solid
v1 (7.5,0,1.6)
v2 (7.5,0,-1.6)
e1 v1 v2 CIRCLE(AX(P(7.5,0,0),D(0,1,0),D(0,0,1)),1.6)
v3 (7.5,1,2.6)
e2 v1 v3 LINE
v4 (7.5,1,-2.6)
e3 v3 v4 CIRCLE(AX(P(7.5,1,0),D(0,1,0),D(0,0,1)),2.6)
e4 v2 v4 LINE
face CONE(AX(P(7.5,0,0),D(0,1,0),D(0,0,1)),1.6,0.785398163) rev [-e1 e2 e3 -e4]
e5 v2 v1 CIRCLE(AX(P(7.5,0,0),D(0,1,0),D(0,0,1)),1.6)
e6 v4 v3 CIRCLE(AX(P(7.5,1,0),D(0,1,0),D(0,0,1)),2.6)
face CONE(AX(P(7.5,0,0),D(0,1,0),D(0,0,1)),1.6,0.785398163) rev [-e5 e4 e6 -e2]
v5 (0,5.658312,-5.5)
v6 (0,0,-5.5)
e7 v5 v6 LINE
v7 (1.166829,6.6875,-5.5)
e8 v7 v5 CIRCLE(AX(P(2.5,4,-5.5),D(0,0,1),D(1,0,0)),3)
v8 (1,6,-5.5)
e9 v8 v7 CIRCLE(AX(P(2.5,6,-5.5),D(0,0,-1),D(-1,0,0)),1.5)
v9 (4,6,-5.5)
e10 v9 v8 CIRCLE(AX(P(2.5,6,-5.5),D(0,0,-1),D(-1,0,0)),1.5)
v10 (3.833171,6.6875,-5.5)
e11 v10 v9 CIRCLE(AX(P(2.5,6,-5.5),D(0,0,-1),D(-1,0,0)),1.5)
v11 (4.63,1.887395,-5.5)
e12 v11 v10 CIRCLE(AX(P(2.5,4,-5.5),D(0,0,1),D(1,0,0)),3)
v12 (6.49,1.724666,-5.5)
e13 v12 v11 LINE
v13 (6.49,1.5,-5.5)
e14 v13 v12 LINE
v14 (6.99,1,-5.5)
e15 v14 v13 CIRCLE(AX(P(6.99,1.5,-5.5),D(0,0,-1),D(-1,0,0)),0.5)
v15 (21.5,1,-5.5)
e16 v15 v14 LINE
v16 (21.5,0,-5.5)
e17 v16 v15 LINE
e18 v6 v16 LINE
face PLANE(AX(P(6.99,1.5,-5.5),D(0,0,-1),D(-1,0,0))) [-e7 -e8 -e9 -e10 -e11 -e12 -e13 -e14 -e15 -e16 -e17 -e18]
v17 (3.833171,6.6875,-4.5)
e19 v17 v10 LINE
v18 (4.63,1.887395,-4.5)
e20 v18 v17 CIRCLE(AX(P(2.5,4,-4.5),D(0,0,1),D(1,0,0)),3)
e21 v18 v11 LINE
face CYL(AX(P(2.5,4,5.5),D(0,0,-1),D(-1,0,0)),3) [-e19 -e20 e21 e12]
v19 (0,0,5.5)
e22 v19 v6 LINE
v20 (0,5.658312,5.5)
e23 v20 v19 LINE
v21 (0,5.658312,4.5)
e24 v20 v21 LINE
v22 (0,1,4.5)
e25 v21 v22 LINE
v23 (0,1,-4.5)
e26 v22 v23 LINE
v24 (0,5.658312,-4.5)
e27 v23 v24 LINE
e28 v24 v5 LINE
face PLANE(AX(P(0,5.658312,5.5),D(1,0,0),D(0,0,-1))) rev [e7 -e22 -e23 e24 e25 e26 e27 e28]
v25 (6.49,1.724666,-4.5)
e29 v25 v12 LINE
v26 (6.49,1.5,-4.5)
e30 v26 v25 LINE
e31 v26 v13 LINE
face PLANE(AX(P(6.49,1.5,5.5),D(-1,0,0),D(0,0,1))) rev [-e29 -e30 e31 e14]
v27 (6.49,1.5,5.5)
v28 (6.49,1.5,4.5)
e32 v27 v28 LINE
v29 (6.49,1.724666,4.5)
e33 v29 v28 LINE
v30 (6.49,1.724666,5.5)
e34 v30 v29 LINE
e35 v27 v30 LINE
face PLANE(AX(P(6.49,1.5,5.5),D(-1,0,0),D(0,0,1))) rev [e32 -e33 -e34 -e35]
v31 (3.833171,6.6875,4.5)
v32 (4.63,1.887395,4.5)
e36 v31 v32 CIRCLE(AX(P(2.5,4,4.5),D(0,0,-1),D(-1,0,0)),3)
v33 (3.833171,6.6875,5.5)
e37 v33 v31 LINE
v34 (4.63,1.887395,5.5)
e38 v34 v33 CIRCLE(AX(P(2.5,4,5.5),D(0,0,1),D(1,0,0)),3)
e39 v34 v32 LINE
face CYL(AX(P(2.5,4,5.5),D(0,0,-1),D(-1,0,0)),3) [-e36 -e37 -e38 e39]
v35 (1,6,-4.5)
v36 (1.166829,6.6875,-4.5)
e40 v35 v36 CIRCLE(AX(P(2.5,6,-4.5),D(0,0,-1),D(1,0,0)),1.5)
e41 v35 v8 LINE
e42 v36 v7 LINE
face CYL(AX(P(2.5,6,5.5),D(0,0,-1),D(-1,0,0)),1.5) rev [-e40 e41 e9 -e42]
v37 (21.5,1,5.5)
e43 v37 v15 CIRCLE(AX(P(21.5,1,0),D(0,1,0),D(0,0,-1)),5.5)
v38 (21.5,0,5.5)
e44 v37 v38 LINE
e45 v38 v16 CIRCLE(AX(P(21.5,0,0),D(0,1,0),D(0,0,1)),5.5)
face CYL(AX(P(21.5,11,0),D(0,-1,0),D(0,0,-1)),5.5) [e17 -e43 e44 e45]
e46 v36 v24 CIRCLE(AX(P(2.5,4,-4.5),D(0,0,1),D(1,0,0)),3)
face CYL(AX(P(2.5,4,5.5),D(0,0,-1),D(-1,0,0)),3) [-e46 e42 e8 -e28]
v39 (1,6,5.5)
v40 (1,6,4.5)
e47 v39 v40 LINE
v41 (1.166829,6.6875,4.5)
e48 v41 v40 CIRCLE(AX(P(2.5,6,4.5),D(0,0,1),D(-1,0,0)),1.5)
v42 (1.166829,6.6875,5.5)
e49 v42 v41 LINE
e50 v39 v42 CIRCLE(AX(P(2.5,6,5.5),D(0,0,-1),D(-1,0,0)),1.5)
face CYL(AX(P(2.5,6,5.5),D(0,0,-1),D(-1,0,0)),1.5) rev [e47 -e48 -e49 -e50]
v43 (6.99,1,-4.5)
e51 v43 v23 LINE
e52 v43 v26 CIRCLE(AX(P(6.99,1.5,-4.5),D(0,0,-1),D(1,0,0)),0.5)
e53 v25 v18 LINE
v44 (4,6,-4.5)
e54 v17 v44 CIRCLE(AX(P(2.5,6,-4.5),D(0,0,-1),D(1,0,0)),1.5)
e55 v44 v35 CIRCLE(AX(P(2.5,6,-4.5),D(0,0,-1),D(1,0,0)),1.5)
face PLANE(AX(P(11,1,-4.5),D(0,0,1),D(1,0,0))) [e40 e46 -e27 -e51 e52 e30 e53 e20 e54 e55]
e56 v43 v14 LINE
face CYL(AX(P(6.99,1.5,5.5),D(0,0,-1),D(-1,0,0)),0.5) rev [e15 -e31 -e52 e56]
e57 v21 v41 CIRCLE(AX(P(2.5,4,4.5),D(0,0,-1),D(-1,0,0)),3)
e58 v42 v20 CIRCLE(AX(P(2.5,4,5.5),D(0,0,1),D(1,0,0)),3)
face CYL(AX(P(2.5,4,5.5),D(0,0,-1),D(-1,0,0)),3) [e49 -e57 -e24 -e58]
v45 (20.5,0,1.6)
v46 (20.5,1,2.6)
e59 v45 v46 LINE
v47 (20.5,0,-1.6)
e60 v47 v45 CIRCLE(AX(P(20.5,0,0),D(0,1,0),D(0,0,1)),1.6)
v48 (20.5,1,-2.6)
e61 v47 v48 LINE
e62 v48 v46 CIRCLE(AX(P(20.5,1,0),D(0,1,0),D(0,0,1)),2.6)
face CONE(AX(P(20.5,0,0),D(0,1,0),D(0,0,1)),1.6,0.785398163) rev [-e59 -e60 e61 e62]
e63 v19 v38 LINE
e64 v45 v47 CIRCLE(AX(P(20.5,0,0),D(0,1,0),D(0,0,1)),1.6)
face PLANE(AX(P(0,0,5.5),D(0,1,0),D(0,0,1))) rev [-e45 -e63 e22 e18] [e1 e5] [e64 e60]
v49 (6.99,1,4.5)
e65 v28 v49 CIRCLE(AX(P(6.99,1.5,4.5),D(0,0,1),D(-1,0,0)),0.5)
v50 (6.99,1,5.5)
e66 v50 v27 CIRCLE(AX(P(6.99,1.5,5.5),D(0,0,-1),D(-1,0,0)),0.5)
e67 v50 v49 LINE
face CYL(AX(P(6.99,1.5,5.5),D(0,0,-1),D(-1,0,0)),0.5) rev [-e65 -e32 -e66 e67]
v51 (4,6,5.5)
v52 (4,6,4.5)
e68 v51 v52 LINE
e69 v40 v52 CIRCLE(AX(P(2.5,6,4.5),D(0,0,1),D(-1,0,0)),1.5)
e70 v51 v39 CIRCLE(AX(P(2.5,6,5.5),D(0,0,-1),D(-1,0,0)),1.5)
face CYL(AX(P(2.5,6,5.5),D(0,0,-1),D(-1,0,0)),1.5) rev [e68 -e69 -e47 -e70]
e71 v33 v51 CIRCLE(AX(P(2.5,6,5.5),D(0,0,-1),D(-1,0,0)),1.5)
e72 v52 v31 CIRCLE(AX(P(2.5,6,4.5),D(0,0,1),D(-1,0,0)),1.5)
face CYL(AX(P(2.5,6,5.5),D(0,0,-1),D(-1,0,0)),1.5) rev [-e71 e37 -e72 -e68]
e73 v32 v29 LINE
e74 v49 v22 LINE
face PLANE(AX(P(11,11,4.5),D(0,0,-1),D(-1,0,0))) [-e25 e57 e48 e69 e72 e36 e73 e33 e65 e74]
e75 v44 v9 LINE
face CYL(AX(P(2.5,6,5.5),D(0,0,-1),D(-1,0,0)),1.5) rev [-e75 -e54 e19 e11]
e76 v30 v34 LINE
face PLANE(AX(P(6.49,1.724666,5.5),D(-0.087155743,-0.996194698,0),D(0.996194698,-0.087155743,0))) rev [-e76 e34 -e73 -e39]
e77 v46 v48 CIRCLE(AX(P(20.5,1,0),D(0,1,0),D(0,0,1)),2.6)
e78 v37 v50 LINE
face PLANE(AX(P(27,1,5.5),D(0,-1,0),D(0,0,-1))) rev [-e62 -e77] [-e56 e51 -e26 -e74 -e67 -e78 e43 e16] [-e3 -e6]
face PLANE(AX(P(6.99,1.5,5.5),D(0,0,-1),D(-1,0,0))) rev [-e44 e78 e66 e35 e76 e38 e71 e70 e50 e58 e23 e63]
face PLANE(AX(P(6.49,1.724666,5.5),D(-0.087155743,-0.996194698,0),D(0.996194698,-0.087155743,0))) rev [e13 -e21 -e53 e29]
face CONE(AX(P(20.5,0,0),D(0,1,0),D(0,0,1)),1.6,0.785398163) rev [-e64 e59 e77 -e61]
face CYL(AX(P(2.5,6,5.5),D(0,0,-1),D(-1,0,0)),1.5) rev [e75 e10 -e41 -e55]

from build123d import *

# Parameters (mm, degrees)
EXTRUDE_1_DEPTH      = 5.5
EXTRUDE_1_DEPTH_BACK = 5.5
SKETCH_2_W           = 108
SKETCH_2_H           = 22
CUT_EXTRUDE_1_DEPTH  = 11
SKETCH_4_W           = 9
SKETCH_4_H           = 10
CUT_EXTRUDE_2_DEPTH  = 11


with BuildPart() as part:
    # 草图1 → 凸台-拉伸1 (new, two sides: drawn at the far end of the back side and taken through both)
    with BuildSketch(Plane.XY.offset(-EXTRUDE_1_DEPTH_BACK)):
        with BuildLine():
            Line((0, 0), (27, 0))
            Line((27, 0), (27, 1))
            Line((27, 1), (6.99, 1))
            ThreePointArc((6.99, 1), (6.636446609, 1.146446609), (6.49, 1.5))
            Line((6.49, 1.5), (6.49, 1.724666059))
            Line((6.49, 1.724666059), (4.63, 1.887394973))
            ThreePointArc((4.63, 1.887394973), (5.459499899, 4.491284383), (3.833170563, 6.6875))
            ThreePointArc((3.833170563, 6.6875), (2.5, 4.5), (1.166829437, 6.6875))
            ThreePointArc((1.166829437, 6.6875), (0.515533844, 6.249865346), (0, 5.658312395))
            Line((0, 5.658312395), (0, 0))
        make_face()
    extrude(amount=EXTRUDE_1_DEPTH + EXTRUDE_1_DEPTH_BACK)

    # 草图2 → 切除-拉伸1 (cut)
    with BuildSketch(Plane(origin=(0, 0, 0), x_dir=(1, 0, 0), z_dir=(0, 1, 0))):
        Rectangle(SKETCH_2_W, SKETCH_2_H)
        with BuildLine():
            Line((0, 5.5), (0, -5.5))
            Line((0, -5.5), (21.5, -5.5))
            ThreePointArc((21.5, -5.5), (27, 0), (21.5, 5.5))
            Line((21.5, 5.5), (0, 5.5))
        make_face(mode=Mode.SUBTRACT)
    extrude(amount=CUT_EXTRUDE_1_DEPTH, mode=Mode.SUBTRACT)

    # 草图4 → 切除-拉伸2 (cut)
    with BuildSketch(Plane(origin=(0, 0, 0), x_dir=(0, 0, -1), z_dir=(1, 0, 0))):
        with Locations((0, 6)):
            Rectangle(SKETCH_4_W, SKETCH_4_H)
    extrude(amount=CUT_EXTRUDE_2_DEPTH, mode=Mode.SUBTRACT)

    # 草图3 → 切除-旋转1 (revolve, cut)
    with BuildSketch(Plane.XY, mode=Mode.PRIVATE) as cut_revolve_1_sk:
        Polygon((7.5, 1), (10.1, 1), (9.1, 0), (7.5, 0), align=None)
    revolve(cut_revolve_1_sk.sketch.rotate(Axis((7.5, 0, 0), (0, 1, 0)), 270), axis=Axis((7.5, 0, 0), (0, 1, 0)), mode=Mode.SUBTRACT)

    # 草图5 → 切除-旋转2 (revolve, cut)
    with BuildSketch(Plane.XY, mode=Mode.PRIVATE) as cut_revolve_2_sk:
        Polygon((20.5, 1), (23.1, 1), (22.1, 0), (20.5, 0), align=None)
    revolve(cut_revolve_2_sk.sketch.rotate(Axis((20.5, 0, 0), (0, 1, 0)), 270), axis=Axis((20.5, 0, 0), (0, 1, 0)), mode=Mode.SUBTRACT)


solid = part.part
